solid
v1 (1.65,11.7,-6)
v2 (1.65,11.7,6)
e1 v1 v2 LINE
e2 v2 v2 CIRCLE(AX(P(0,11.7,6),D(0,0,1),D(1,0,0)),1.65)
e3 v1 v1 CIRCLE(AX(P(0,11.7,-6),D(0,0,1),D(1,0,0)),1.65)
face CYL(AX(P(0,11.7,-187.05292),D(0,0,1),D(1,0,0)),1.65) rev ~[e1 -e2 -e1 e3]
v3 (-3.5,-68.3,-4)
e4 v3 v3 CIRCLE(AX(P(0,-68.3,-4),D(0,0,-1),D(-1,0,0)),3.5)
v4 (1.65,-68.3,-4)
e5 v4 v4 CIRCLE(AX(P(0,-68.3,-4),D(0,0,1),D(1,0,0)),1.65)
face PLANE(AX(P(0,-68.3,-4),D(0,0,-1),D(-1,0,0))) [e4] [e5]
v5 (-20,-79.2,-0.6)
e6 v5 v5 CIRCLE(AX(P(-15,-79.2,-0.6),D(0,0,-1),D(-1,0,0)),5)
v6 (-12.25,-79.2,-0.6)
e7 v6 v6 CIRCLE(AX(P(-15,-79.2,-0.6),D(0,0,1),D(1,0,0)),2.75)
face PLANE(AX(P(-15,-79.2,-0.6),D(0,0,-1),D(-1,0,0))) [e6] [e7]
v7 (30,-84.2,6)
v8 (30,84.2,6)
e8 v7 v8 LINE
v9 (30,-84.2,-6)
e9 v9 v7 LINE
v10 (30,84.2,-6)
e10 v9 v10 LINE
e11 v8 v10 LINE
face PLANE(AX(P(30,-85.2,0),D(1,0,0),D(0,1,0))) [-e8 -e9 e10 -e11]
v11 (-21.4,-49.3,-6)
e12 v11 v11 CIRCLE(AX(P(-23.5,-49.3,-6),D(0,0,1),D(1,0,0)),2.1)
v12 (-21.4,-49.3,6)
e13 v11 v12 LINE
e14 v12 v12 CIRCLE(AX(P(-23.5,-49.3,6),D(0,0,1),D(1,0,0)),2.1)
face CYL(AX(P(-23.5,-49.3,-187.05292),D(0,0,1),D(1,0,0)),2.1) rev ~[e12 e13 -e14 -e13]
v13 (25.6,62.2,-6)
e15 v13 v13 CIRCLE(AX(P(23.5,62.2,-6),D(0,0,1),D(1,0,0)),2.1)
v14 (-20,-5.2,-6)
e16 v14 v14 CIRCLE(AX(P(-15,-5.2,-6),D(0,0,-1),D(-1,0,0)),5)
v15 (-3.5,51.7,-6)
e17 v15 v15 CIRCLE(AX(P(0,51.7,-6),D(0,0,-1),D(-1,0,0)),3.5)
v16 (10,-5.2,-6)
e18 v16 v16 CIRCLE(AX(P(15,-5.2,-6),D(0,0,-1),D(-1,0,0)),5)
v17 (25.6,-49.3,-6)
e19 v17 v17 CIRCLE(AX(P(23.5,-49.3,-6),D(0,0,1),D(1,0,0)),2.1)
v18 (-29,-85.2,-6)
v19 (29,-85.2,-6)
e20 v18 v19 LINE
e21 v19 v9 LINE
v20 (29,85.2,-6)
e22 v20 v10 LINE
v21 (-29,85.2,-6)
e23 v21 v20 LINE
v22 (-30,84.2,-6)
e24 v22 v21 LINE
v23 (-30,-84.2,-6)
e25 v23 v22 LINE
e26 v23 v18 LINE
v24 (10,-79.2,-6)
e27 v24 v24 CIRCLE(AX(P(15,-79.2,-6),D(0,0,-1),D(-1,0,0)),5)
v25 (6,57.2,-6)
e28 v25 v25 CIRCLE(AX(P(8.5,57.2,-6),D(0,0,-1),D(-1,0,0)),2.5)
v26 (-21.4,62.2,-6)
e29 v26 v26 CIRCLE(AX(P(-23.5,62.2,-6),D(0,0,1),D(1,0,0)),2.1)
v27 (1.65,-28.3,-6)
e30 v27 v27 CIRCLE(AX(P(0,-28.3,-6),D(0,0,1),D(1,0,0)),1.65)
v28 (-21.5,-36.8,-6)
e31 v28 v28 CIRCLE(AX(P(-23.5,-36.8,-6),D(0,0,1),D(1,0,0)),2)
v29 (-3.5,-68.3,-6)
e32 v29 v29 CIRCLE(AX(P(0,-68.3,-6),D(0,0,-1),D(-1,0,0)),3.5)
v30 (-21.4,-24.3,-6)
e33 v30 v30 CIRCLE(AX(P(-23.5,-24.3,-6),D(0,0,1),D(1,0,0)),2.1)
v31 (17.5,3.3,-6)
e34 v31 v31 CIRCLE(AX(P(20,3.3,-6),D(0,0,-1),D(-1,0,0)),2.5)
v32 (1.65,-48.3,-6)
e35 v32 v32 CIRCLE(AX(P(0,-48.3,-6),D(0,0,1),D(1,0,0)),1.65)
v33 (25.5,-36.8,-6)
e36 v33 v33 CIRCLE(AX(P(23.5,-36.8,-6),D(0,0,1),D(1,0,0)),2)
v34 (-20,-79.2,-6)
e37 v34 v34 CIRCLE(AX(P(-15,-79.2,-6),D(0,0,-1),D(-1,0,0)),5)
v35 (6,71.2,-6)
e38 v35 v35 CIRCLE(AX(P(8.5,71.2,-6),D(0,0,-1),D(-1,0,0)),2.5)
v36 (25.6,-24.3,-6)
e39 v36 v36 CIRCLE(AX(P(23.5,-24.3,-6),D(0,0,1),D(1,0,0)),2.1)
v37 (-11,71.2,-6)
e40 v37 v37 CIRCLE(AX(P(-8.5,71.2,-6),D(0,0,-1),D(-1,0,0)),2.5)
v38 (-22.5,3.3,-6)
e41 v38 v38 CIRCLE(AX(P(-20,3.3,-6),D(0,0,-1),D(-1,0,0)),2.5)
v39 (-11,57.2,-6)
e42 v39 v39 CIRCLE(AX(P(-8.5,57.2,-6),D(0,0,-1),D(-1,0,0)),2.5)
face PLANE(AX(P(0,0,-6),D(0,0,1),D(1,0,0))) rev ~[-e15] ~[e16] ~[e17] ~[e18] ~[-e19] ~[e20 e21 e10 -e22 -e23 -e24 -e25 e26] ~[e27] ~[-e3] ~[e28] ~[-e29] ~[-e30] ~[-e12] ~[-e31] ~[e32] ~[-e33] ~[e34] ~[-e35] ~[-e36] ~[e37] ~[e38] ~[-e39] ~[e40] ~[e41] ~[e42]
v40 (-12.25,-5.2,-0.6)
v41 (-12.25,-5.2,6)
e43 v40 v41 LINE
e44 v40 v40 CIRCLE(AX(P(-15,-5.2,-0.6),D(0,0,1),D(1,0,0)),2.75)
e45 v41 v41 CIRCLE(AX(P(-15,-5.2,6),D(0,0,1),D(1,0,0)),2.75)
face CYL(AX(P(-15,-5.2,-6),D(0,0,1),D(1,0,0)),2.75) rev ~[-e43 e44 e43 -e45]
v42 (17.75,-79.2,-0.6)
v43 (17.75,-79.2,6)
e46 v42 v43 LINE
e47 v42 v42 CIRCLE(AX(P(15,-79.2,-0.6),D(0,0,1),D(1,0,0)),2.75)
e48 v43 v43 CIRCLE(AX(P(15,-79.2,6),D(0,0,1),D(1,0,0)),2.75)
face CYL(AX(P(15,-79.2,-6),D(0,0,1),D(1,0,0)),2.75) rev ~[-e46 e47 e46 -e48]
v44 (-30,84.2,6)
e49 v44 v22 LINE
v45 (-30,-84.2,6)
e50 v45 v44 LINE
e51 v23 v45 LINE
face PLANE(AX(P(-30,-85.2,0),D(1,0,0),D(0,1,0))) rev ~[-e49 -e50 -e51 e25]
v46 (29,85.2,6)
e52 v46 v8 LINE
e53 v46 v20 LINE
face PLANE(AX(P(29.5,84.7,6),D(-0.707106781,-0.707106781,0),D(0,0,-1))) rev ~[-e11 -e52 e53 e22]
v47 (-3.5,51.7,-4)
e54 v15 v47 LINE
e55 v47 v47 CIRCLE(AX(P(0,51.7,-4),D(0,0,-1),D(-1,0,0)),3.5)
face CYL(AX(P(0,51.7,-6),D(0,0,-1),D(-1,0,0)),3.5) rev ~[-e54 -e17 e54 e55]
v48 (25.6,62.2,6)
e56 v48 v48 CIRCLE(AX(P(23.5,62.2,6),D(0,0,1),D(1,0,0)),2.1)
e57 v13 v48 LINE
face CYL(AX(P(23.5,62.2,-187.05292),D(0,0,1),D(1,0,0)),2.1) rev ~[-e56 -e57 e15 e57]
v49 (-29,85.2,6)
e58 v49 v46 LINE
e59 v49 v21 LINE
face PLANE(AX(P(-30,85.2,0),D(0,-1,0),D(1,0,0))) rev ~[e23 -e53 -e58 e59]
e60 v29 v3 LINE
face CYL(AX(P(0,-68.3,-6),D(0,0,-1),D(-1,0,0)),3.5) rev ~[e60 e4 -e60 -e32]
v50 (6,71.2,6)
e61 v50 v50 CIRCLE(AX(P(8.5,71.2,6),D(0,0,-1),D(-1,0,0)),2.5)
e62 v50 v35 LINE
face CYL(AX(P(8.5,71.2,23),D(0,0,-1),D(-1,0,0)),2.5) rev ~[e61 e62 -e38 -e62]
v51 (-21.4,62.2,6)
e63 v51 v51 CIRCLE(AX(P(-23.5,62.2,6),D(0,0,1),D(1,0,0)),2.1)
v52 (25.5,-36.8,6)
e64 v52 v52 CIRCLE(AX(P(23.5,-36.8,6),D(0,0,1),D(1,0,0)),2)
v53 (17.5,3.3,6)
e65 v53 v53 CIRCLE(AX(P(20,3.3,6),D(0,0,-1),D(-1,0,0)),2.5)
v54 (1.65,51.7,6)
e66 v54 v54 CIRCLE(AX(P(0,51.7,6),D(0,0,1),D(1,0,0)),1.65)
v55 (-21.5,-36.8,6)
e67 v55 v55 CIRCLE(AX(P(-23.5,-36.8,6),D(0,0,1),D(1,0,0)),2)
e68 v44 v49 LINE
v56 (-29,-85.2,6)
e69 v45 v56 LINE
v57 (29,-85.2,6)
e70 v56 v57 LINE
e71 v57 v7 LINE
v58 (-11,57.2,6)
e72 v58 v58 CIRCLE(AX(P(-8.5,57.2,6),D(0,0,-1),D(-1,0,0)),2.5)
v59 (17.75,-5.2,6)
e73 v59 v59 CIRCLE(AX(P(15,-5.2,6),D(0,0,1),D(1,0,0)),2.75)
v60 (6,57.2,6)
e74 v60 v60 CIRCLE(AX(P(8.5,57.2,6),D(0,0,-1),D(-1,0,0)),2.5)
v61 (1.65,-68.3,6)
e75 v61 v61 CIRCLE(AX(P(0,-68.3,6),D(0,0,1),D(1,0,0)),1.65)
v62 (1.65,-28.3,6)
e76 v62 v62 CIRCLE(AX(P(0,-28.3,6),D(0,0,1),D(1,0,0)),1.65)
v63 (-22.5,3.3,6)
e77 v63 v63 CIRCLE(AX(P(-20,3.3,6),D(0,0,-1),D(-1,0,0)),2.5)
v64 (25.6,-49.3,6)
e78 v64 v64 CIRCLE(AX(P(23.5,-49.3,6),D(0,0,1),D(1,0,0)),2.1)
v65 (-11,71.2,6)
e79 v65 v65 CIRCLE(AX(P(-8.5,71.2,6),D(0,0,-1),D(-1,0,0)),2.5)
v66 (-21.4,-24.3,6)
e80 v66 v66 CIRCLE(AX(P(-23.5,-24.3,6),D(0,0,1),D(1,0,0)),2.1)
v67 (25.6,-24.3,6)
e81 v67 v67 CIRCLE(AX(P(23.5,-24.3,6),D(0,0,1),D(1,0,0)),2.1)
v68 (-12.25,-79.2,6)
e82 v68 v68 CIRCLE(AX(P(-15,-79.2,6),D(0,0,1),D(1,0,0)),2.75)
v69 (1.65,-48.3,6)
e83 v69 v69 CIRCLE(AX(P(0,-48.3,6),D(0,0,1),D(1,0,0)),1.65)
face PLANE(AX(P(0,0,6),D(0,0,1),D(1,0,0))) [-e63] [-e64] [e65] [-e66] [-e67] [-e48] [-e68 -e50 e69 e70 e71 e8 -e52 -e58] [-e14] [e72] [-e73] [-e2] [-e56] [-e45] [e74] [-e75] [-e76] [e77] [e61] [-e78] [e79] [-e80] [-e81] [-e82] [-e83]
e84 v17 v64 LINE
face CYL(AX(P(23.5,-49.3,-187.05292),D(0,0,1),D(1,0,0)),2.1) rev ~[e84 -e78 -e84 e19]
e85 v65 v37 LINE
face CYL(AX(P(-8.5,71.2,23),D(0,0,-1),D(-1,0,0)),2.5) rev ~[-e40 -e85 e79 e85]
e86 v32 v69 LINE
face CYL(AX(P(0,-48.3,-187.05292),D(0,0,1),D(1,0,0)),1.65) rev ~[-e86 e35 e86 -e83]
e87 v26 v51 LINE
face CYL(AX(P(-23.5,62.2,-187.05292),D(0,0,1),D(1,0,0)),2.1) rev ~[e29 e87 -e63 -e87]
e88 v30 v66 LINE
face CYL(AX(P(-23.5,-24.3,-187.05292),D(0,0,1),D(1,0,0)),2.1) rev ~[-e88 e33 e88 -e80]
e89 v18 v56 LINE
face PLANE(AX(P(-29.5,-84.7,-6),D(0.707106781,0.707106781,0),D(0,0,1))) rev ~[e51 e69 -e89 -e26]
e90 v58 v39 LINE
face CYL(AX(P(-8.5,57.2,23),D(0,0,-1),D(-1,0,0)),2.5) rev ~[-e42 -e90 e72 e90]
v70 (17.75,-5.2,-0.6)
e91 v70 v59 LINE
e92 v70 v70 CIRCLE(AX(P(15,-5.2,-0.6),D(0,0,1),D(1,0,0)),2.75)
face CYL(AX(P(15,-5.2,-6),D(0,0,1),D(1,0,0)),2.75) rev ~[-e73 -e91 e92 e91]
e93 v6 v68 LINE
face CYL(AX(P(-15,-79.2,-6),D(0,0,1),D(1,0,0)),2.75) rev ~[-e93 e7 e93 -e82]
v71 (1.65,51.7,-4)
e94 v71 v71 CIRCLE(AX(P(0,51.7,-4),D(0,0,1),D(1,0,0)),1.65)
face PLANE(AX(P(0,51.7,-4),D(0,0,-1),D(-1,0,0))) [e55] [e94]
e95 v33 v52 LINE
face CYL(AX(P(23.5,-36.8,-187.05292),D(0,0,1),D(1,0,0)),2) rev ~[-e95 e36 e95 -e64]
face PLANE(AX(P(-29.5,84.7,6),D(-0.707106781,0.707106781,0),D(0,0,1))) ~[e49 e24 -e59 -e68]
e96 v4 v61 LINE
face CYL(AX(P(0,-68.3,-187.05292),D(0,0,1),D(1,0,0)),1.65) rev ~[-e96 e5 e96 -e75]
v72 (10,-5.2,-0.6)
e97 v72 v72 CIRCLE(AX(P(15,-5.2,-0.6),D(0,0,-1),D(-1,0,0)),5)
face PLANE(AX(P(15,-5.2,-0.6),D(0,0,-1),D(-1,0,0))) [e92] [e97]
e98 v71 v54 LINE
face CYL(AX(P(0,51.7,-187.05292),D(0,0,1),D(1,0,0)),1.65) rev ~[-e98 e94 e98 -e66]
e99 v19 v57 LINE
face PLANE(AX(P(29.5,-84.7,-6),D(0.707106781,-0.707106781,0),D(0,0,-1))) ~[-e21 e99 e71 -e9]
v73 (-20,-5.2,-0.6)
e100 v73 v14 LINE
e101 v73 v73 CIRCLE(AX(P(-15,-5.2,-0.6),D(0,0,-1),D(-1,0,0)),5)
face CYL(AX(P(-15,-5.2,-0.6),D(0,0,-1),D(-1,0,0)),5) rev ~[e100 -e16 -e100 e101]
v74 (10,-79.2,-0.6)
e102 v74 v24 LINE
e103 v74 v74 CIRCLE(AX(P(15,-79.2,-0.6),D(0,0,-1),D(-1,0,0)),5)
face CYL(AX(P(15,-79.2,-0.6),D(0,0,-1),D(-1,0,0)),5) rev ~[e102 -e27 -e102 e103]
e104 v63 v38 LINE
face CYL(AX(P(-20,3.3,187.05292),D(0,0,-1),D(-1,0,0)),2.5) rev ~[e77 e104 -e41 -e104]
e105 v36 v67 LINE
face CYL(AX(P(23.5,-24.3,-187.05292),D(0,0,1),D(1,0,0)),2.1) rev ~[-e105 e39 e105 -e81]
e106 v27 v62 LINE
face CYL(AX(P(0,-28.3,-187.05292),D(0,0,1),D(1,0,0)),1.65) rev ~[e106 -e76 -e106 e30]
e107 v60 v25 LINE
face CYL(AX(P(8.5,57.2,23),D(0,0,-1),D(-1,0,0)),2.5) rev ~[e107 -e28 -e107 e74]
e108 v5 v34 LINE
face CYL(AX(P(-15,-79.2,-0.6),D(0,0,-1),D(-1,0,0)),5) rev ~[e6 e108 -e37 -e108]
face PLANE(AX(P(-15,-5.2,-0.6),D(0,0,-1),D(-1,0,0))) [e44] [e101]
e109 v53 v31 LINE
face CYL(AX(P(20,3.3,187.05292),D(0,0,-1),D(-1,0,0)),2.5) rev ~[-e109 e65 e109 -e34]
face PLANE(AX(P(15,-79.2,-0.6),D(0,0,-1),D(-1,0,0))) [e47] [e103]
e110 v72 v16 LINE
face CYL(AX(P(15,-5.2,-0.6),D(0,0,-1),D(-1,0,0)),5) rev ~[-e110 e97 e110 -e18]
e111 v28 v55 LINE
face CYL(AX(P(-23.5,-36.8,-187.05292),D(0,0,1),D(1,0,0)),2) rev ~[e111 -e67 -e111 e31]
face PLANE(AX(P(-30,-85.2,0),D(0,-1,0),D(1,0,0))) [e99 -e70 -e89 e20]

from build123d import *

# Parameters (mm, degrees)
SKETCH1_W                                           = 60
SKETCH1_H                                           = 170.4
BOSS_EXTRUDE1_DEPTH                                 = 6
CBORE_FOR_M5_HEX_SOCKET_HEAD_CAP_SCREW1_D           = 5.5
CBORE_FOR_M5_HEX_SOCKET_HEAD_CAP_SCREW1_CBORE_D     = 10
CBORE_FOR_M5_HEX_SOCKET_HEAD_CAP_SCREW1_CBORE_DEPTH = 5.4
BLIND_PIN_HOLE0_D                                   = 5
M4_TAPPED_HOLE1_D                                   = 3.3
SKETCH11_R                                          = 3.5
CUT_EXTRUDE1_DEPTH                                  = 2
M6_TAPPED_HOLE1_D                                   = 5
M6_TAPPED_HOLE1_DEPTH                               = 17
M6_TAPPED_HOLE1_TIP                                 = 1.502151548
CHAMFER1_SIZE                                       = 1
BLIND_PIN_HOLE1_D                                   = 4
M5_TAPPED_HOLE1_D                                   = 4.2


with BuildPart() as part:
    # Sketch1 → Boss-Extrude1 (new, symmetric)
    with BuildSketch(Plane.XY):
        Rectangle(SKETCH1_W, SKETCH1_H)
    extrude(amount=BOSS_EXTRUDE1_DEPTH, both=True)

    # CBORE for M5 Hex Socket Head Cap Screw1 (through all)
    with Locations(Plane(origin=(0, 0, -6), x_dir=(-1, 0, 0), z_dir=(0, 0, -1))):
        with Locations((15, -5.2), (-15, -5.2), (15, -79.2), (-15, -79.2)):
            CounterBoreHole(CBORE_FOR_M5_HEX_SOCKET_HEAD_CAP_SCREW1_D / 2, CBORE_FOR_M5_HEX_SOCKET_HEAD_CAP_SCREW1_CBORE_D / 2, CBORE_FOR_M5_HEX_SOCKET_HEAD_CAP_SCREW1_CBORE_DEPTH)

    # Blind pin hole0 (through all)
    with Locations(Plane.XY.offset(6)):
        with Locations((20, 3.3), (-20, 3.3)):
            Hole(BLIND_PIN_HOLE0_D / 2)

    # M4 Tapped Hole1 (through all)
    with Locations(Plane(origin=(0, 0, -6), x_dir=(-1, 0, 0), z_dir=(0, 0, -1))):
        with Locations((0, 11.7), (0, -28.3), (0, -48.3), (0, -68.3), (0, 51.7)):
            Hole(M4_TAPPED_HOLE1_D / 2)

    # Sketch11 → Cut-Extrude1 (cut)
    with BuildSketch(Plane(origin=(0, 0, -6), x_dir=(-1, 0, 0), z_dir=(0, 0, -1))):
        with Locations((0, 51.7)):
            Circle(SKETCH11_R)
        with Locations((0, -68.3)):
            Circle(SKETCH11_R)
    extrude(amount=-CUT_EXTRUDE1_DEPTH, mode=Mode.SUBTRACT)

    # M6 Tapped Hole1
    with Locations(Plane.XY.offset(6)):
        with Locations((8.5, 57.2), (-8.5, 57.2), (8.5, 71.2), (-8.5, 71.2)):
            Hole(M6_TAPPED_HOLE1_D / 2, depth=M6_TAPPED_HOLE1_DEPTH)
            with Locations((0, 0, -(M6_TAPPED_HOLE1_DEPTH + M6_TAPPED_HOLE1_TIP / 2))):  # 118° drill point
                Cone(0, M6_TAPPED_HOLE1_D / 2, M6_TAPPED_HOLE1_TIP, mode=Mode.SUBTRACT)

    # Chamfer1
    chamfer1_edges = [part.edges().sort_by_distance(p)[0] for p in [
        (30, -85.2, 0),
        (-30, -85.2, 0),
        (-30, 85.2, 0),
        (30, 85.2, 0),
    ]]
    chamfer(chamfer1_edges, length=CHAMFER1_SIZE)

    # Blind pin hole1 (through all)
    with Locations(Plane(origin=(0, 0, -6), x_dir=(-1, 0, 0), z_dir=(0, 0, -1))):
        with Locations((23.5, -36.8), (-23.5, -36.8)):
            Hole(BLIND_PIN_HOLE1_D / 2)

    # M5 Tapped Hole1 (through all)
    with Locations(Plane(origin=(0, 0, -6), x_dir=(-1, 0, 0), z_dir=(0, 0, -1))):
        with Locations((23.5, 62.2), (-23.5, -24.3), (-23.5, -49.3), (23.5, -49.3), (23.5, -24.3), (-23.5, 62.2)):
            Hole(M5_TAPPED_HOLE1_D / 2)


solid = part.part
